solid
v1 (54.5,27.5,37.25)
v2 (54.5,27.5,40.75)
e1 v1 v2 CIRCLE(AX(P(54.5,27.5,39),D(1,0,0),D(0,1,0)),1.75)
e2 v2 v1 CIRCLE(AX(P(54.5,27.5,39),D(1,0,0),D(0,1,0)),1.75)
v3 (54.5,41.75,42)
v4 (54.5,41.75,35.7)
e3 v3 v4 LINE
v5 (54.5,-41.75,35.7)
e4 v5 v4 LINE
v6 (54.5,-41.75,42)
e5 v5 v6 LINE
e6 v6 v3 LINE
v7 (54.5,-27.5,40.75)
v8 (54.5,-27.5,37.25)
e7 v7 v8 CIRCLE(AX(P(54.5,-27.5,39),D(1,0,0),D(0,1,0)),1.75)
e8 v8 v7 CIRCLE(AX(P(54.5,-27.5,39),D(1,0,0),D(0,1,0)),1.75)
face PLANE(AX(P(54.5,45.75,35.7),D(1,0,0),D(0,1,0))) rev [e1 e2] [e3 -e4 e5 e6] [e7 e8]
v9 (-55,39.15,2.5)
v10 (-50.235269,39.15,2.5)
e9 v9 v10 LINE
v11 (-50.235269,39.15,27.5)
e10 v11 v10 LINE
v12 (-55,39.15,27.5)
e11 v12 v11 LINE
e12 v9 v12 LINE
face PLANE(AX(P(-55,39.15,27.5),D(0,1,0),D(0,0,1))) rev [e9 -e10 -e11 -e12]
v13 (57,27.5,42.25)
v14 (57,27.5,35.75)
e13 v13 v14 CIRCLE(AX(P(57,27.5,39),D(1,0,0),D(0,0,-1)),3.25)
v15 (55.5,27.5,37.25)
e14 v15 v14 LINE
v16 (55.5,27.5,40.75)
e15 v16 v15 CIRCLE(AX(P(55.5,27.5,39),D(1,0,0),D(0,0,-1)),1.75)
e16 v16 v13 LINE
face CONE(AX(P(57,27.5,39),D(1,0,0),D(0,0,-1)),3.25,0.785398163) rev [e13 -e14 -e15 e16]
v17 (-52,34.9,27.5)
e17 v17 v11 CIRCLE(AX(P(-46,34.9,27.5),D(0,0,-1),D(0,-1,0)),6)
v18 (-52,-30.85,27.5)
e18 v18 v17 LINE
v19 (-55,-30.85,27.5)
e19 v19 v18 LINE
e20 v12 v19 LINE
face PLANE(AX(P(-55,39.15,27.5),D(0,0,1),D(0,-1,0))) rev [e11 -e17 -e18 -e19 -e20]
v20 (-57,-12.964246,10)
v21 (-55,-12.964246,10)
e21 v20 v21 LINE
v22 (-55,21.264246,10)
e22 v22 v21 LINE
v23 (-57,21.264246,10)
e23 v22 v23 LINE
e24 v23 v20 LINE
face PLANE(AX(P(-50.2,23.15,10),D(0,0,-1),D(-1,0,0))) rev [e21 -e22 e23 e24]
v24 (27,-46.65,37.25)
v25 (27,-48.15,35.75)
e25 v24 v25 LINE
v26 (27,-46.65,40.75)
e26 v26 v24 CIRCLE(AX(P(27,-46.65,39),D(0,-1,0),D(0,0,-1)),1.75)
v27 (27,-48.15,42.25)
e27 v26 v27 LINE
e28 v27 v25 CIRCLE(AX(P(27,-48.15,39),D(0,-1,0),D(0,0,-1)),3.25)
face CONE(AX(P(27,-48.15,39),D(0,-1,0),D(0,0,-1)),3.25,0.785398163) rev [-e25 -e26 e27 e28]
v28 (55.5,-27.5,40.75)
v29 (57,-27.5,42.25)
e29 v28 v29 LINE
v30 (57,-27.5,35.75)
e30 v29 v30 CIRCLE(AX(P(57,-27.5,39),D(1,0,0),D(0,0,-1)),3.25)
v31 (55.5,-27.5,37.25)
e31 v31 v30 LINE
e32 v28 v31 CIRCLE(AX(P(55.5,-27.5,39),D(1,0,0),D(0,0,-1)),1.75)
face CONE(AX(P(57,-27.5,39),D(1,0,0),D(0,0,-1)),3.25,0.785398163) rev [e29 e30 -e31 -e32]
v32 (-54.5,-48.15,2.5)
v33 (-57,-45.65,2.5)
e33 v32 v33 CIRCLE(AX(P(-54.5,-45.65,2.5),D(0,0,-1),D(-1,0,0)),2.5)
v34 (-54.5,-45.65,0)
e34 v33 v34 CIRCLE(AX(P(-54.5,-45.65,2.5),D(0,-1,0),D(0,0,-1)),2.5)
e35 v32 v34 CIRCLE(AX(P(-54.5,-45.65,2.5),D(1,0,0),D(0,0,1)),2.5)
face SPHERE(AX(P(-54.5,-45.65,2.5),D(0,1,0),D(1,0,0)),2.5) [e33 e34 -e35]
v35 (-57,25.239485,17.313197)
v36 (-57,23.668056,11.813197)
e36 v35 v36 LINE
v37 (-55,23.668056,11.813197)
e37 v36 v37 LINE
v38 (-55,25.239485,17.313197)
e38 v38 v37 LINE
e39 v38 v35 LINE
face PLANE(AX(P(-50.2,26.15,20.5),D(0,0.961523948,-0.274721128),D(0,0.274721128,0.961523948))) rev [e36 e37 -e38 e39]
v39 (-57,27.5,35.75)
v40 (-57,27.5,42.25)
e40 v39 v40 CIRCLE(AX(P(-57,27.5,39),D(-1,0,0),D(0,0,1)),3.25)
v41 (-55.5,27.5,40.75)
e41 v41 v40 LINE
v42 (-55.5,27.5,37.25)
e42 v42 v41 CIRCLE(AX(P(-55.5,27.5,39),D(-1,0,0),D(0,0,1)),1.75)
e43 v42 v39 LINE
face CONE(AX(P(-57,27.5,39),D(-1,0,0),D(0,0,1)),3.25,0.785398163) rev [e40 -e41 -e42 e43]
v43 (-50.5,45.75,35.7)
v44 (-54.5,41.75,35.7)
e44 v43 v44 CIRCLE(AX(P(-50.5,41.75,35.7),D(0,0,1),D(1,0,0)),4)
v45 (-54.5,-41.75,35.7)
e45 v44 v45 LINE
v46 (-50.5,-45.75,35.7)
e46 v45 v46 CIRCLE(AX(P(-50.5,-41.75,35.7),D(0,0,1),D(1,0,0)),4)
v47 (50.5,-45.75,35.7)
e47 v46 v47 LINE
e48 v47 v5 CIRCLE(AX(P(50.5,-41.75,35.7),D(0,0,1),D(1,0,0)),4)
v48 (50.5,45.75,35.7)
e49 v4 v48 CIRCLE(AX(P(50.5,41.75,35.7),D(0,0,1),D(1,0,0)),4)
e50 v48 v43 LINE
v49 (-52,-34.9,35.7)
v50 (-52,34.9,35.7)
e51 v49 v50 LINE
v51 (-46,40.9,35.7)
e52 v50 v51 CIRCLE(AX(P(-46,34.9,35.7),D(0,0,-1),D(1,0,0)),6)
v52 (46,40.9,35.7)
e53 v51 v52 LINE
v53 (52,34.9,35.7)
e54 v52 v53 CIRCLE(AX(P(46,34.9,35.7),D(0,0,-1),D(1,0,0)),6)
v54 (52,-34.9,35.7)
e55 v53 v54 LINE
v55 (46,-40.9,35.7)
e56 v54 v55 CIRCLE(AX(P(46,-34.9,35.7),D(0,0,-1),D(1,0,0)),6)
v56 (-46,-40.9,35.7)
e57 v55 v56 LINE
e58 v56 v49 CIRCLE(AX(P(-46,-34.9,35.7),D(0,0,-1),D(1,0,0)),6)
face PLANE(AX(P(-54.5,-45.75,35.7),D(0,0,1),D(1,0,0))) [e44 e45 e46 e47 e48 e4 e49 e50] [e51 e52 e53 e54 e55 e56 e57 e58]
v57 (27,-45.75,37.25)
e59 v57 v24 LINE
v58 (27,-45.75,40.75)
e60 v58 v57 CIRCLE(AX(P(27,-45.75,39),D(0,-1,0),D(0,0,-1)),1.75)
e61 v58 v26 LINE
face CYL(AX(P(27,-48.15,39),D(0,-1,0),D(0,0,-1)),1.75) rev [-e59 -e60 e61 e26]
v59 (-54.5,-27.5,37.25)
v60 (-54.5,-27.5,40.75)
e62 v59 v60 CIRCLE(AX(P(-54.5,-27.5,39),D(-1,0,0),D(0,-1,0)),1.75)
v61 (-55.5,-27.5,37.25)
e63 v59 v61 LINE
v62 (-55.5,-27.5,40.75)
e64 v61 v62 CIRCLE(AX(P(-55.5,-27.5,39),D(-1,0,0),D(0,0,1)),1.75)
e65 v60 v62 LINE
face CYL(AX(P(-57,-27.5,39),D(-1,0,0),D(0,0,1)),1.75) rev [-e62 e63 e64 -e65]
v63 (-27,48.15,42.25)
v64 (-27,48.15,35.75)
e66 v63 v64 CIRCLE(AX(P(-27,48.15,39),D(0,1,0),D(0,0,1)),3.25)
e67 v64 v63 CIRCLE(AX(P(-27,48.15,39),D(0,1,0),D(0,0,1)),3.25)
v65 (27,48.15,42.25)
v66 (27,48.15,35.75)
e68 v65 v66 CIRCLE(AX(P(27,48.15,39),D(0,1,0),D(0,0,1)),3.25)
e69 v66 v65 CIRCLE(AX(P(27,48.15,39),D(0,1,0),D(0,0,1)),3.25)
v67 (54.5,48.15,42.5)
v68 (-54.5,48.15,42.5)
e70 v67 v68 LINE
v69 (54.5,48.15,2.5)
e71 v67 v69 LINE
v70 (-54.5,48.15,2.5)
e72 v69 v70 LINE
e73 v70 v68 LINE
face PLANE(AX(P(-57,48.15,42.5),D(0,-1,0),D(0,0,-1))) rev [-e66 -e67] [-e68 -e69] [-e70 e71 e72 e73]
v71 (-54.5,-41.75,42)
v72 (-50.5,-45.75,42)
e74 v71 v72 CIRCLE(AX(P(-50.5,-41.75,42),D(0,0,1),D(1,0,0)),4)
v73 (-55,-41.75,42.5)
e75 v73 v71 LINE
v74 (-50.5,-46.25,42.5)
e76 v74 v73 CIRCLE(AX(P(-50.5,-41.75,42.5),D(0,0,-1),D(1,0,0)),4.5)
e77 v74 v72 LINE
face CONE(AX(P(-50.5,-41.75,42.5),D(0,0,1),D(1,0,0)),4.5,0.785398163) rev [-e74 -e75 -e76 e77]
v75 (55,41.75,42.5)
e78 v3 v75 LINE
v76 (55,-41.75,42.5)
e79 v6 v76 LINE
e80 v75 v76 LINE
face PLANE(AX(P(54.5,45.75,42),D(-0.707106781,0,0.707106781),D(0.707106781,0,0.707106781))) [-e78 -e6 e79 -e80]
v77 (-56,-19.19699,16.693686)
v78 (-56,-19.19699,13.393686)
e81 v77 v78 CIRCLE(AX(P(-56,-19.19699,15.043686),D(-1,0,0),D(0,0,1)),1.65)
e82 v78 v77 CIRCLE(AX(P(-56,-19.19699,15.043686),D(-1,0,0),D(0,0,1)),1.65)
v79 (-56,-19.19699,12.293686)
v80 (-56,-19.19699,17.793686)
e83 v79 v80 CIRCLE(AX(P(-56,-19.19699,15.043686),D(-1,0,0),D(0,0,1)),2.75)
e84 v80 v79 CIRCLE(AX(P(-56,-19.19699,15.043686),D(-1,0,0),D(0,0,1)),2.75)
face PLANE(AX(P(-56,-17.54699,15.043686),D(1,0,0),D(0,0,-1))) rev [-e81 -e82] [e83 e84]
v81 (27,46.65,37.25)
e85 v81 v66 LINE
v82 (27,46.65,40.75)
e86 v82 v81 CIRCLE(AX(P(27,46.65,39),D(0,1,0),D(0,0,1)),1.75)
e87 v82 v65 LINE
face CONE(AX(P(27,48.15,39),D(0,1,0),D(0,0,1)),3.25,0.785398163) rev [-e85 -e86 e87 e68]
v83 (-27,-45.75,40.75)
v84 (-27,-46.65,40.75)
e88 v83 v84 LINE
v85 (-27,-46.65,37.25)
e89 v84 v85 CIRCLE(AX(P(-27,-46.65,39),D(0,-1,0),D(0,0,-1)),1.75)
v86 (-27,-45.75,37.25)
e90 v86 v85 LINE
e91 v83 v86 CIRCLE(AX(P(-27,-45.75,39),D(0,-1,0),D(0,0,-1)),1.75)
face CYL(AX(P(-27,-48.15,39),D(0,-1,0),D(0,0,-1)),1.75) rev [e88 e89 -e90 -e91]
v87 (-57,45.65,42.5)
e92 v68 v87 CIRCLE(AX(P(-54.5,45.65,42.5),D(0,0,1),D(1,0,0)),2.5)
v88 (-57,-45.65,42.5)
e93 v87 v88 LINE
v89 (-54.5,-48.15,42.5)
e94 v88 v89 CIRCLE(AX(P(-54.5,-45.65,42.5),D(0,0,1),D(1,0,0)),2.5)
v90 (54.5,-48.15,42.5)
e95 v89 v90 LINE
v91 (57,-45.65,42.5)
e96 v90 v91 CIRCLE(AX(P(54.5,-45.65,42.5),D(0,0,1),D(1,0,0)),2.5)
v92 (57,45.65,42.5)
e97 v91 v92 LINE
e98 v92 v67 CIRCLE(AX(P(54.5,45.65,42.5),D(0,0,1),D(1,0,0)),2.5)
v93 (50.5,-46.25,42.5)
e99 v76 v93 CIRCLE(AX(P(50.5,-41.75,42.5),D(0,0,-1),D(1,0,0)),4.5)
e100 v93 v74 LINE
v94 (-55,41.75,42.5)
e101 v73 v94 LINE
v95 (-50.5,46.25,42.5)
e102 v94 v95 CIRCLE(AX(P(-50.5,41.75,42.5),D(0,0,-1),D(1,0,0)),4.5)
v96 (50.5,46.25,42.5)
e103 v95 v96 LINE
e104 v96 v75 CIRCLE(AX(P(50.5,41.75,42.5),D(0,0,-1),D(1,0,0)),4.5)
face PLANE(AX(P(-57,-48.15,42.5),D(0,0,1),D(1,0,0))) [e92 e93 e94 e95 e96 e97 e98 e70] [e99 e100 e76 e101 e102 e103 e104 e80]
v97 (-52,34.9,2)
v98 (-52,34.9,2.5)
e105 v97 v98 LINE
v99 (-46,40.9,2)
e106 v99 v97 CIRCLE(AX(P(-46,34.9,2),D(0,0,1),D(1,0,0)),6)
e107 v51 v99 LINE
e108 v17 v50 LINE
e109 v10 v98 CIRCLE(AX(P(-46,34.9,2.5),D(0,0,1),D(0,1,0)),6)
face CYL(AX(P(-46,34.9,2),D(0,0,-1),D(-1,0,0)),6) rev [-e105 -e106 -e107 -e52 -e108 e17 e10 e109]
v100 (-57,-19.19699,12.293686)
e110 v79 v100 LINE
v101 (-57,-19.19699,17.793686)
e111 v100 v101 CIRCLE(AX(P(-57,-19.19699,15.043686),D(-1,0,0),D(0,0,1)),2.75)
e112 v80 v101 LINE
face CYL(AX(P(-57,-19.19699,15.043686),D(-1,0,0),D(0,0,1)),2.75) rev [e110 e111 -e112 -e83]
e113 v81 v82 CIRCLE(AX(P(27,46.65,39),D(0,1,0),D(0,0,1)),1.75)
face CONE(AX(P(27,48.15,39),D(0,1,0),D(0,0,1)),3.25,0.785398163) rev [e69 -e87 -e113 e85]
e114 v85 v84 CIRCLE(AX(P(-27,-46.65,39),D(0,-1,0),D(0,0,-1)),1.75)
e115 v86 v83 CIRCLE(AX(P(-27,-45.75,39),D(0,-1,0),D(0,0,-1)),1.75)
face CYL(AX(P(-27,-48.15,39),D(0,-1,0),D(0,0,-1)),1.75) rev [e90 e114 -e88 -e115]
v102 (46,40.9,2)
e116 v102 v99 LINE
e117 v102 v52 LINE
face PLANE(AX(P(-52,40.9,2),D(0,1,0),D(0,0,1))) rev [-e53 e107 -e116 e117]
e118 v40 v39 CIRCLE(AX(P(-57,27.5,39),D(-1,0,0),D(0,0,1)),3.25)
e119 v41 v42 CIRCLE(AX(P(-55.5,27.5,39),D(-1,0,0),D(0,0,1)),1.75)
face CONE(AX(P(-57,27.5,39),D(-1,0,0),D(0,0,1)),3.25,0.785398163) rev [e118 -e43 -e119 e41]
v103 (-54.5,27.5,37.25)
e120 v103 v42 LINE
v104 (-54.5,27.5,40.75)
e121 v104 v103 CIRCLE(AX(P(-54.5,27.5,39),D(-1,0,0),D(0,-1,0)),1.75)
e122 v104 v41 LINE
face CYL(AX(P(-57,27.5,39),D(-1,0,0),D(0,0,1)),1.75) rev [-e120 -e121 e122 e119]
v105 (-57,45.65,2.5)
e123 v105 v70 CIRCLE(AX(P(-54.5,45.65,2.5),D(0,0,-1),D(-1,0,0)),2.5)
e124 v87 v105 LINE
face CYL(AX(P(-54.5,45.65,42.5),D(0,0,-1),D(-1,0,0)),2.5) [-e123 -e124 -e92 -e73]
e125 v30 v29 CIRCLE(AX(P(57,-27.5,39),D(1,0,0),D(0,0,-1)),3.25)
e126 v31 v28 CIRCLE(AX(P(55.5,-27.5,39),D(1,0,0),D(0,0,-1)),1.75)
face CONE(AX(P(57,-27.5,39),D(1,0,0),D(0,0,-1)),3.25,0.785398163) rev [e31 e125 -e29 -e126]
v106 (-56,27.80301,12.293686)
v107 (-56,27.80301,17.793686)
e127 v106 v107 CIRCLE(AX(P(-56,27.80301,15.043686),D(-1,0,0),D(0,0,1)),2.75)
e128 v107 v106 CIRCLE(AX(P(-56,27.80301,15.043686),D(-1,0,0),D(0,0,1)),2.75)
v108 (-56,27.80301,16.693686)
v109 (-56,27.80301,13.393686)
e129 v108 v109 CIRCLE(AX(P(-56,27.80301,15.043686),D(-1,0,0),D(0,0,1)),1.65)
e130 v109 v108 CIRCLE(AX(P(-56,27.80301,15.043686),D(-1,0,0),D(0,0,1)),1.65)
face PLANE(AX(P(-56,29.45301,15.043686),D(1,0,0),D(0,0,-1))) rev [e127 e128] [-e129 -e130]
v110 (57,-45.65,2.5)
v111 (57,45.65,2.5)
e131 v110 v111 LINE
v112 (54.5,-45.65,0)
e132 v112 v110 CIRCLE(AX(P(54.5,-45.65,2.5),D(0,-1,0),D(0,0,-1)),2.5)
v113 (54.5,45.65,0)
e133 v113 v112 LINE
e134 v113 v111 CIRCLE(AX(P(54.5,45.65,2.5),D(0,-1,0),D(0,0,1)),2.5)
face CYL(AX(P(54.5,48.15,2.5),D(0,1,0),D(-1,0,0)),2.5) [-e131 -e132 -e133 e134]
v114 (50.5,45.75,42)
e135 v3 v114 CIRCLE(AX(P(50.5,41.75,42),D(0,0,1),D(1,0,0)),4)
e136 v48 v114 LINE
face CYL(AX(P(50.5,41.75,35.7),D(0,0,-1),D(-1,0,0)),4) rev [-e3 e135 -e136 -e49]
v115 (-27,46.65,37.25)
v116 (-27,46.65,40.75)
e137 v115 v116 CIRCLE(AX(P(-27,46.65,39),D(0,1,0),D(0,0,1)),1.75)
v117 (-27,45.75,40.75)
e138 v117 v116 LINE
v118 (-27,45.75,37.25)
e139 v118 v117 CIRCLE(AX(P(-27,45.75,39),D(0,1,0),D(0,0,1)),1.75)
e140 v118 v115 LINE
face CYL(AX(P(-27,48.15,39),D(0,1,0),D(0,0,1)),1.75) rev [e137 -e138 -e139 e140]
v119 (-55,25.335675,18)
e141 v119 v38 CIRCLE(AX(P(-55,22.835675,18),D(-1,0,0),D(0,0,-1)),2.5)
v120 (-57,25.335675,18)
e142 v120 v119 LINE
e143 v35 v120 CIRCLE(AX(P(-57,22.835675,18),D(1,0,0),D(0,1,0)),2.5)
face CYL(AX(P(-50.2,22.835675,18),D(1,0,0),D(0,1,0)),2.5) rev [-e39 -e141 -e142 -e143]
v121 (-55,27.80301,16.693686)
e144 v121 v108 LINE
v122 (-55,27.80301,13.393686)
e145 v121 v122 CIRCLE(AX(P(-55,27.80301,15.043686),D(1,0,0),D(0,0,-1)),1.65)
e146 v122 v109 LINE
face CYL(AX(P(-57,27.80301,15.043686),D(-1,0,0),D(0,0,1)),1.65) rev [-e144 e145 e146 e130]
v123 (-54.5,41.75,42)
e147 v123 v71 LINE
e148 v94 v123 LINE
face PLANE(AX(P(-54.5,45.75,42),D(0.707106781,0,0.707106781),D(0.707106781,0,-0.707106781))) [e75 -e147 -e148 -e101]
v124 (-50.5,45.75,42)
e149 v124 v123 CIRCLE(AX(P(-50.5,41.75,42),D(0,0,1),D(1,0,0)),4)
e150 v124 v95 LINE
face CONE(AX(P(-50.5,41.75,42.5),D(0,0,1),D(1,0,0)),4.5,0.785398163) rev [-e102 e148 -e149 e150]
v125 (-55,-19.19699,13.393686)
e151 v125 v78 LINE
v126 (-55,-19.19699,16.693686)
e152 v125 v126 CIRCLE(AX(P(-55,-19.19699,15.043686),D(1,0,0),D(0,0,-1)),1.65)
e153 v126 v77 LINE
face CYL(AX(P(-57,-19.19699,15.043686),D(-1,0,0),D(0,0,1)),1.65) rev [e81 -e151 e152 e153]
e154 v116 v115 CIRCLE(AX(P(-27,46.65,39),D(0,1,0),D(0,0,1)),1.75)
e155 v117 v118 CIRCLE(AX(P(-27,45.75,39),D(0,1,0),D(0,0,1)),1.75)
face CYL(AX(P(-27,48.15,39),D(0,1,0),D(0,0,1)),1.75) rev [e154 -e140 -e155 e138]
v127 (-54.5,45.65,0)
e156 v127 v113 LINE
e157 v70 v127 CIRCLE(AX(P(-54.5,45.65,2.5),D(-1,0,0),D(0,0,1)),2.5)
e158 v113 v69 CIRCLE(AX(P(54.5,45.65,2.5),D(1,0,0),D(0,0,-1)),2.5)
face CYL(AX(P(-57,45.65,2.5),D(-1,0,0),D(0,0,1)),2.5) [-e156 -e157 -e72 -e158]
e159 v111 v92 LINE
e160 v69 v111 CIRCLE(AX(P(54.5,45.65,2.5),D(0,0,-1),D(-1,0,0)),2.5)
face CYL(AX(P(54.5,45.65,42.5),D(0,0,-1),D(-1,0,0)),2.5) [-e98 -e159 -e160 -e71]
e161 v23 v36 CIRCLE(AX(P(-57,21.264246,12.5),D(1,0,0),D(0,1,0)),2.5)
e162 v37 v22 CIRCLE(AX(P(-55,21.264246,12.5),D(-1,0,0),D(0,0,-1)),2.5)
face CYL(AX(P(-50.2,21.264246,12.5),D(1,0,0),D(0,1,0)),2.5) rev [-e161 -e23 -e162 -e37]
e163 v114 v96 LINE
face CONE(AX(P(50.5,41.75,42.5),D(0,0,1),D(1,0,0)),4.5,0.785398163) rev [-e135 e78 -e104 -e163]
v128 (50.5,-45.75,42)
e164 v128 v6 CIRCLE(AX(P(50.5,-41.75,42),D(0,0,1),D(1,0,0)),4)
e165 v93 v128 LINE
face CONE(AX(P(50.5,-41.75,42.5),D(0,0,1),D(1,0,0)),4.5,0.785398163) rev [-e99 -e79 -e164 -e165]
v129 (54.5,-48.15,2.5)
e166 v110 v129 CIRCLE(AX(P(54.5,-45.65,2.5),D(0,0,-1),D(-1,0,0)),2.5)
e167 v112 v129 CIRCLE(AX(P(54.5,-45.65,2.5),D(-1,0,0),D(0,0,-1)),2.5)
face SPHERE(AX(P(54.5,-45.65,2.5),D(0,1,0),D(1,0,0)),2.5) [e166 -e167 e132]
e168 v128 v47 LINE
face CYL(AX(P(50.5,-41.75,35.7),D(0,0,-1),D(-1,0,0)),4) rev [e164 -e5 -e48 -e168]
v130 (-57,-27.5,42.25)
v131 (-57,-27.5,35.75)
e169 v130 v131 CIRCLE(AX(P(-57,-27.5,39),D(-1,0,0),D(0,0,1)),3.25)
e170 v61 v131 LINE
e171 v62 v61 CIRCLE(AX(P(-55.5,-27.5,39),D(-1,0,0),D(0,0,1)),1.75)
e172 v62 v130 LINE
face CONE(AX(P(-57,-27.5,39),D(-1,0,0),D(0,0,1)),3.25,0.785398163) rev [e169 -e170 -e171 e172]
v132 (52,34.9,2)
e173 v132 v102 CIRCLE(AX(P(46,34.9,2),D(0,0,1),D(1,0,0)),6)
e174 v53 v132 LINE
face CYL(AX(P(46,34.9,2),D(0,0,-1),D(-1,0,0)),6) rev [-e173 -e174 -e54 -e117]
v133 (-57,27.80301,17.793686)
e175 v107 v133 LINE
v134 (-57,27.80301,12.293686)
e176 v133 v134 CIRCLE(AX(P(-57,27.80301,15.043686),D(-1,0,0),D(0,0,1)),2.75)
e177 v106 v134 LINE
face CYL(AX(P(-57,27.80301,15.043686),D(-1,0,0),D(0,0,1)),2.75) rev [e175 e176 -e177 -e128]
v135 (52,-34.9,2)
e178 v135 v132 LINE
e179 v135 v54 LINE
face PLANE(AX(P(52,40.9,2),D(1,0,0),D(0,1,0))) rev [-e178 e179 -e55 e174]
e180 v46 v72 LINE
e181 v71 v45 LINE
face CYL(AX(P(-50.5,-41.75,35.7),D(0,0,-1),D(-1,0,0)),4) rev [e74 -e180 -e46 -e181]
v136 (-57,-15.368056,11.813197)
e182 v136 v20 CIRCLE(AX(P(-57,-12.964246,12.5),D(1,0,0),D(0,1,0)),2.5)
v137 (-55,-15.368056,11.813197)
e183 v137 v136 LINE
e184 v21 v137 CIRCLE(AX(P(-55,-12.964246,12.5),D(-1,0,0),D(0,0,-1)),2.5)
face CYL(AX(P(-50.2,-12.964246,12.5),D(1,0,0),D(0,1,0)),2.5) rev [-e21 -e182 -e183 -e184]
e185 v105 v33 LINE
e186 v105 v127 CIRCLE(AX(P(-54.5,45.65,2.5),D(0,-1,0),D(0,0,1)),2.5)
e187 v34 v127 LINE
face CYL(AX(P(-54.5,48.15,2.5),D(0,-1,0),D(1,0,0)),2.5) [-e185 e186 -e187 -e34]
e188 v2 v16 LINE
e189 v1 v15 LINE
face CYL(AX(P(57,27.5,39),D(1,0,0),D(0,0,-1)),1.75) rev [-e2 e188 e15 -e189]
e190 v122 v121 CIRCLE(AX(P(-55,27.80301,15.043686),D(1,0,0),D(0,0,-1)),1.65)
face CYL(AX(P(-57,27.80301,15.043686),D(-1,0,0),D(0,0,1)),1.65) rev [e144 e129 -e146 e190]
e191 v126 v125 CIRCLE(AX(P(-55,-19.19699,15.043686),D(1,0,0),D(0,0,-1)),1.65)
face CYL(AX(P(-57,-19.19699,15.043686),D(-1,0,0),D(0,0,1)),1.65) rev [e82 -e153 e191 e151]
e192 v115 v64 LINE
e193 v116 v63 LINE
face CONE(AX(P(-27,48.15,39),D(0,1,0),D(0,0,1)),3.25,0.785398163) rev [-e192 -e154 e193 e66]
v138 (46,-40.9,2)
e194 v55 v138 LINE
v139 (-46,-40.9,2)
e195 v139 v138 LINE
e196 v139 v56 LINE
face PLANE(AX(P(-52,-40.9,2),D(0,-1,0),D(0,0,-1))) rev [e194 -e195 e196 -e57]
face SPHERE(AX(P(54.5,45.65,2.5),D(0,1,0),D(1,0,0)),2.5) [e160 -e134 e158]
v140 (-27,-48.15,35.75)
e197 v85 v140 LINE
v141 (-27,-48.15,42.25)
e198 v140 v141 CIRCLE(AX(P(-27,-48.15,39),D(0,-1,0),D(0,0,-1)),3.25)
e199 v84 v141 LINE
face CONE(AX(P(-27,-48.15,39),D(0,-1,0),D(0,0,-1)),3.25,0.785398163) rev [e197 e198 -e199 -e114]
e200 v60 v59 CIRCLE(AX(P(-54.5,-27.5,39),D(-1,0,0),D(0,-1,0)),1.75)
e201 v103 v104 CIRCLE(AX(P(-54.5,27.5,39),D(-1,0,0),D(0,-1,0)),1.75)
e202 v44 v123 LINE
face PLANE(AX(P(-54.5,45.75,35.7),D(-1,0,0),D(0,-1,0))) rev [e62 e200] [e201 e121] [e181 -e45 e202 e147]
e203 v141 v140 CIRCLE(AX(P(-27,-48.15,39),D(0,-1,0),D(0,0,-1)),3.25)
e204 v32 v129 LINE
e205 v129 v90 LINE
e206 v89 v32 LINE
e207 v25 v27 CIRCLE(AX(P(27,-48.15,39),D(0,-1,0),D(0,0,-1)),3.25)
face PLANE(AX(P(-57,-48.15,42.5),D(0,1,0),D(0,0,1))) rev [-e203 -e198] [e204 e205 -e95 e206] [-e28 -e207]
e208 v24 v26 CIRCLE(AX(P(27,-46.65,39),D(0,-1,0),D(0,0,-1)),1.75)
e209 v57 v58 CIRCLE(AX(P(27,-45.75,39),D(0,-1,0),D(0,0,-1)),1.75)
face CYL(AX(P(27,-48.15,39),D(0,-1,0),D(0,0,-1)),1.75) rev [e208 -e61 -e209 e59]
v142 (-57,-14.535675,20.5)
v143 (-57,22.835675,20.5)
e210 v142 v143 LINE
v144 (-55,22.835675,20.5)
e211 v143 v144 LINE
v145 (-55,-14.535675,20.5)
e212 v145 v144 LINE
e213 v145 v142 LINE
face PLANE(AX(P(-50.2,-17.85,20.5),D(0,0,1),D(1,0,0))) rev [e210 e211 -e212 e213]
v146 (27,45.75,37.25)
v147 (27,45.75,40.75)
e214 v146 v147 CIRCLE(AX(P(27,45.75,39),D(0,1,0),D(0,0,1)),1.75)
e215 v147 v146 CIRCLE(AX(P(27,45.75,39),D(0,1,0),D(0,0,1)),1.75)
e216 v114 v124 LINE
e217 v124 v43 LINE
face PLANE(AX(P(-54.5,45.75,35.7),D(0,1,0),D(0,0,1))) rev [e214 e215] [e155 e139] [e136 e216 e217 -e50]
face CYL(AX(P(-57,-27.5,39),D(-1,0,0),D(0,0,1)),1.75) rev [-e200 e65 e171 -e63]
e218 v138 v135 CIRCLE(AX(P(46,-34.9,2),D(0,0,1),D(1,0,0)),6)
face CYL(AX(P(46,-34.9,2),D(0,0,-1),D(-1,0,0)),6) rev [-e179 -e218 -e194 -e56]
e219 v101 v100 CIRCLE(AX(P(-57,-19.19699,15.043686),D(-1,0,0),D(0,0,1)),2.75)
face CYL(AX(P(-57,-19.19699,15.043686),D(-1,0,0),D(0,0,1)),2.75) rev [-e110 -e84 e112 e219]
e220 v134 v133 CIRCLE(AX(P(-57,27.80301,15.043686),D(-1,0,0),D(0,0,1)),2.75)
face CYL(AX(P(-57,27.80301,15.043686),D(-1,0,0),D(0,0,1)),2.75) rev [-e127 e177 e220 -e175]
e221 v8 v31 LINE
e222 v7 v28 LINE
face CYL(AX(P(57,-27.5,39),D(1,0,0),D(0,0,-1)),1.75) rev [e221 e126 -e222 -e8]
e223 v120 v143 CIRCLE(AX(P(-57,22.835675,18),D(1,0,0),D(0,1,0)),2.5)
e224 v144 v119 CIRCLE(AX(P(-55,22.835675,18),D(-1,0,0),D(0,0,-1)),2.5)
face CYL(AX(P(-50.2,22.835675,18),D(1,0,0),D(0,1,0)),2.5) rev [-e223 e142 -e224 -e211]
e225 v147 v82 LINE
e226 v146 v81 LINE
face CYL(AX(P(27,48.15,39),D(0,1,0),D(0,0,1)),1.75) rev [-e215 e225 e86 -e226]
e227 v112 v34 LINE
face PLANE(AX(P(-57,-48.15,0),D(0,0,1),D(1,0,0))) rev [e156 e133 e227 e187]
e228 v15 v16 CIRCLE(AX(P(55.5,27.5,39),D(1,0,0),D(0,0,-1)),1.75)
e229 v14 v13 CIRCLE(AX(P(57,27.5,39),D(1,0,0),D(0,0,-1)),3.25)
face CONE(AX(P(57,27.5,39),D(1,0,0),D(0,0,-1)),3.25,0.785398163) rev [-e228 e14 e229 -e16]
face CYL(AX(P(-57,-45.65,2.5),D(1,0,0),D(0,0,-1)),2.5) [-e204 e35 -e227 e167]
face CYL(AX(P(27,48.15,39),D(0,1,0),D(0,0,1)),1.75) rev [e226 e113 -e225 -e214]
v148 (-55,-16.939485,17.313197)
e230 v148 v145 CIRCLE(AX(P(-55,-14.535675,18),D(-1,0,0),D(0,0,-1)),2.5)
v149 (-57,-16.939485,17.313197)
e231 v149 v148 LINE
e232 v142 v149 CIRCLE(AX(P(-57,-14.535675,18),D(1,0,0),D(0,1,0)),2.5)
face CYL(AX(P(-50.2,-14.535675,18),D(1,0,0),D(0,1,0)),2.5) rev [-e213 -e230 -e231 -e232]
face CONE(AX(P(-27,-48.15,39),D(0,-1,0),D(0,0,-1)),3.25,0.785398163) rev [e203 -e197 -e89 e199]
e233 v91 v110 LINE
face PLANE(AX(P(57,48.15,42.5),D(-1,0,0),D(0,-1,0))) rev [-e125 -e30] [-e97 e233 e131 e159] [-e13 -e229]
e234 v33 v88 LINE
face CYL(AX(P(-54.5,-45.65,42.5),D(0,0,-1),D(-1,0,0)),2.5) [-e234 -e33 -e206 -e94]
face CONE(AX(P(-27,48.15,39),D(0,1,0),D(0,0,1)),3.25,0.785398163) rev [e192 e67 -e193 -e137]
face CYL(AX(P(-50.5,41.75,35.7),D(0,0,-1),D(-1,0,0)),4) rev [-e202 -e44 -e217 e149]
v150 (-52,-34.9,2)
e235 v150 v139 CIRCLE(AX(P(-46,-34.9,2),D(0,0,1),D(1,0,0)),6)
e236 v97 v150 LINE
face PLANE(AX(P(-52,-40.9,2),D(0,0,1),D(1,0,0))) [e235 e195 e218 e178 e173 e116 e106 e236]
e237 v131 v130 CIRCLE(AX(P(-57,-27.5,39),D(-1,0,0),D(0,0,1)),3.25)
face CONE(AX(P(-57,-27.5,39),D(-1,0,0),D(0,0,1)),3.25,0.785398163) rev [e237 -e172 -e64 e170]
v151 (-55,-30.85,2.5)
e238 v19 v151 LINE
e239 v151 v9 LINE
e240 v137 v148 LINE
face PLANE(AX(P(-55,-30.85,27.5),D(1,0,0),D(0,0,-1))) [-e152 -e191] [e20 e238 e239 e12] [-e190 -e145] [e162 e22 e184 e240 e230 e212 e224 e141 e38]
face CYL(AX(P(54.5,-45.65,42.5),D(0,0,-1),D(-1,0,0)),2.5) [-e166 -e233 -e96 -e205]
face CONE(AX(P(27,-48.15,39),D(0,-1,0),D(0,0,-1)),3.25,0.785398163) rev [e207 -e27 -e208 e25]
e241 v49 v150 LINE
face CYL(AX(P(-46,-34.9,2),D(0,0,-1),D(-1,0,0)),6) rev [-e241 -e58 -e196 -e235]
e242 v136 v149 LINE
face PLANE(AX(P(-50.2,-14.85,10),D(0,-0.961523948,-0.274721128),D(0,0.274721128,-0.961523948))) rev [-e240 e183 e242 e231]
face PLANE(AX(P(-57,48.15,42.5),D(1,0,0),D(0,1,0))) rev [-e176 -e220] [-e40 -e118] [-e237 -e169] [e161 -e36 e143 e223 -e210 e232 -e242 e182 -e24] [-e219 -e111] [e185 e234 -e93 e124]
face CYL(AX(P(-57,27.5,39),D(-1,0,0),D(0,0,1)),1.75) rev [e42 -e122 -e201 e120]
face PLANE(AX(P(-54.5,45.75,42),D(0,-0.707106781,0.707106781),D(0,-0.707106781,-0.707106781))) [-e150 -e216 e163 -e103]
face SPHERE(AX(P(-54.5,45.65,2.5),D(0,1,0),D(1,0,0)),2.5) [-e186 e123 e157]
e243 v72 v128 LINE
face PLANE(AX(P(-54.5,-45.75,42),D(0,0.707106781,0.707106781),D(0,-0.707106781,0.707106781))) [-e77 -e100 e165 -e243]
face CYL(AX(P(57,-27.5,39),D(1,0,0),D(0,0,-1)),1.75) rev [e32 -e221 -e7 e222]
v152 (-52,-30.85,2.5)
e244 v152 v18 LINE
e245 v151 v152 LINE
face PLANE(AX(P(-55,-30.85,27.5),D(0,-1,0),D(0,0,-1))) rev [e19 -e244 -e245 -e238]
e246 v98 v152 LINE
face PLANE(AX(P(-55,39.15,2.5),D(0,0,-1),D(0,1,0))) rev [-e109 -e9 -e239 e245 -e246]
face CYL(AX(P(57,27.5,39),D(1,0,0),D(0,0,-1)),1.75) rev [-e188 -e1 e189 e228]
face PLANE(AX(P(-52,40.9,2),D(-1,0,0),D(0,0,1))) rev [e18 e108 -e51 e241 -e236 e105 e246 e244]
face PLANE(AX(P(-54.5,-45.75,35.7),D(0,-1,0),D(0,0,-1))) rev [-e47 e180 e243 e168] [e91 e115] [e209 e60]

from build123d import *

# Parameters (mm, degrees)
SKETCH_1_W                  = 114
SKETCH_1_H                  = 96.3
EXTRUDE_1_DEPTH             = 42.5
SKETCH_2_W                  = 104
SKETCH_2_H                  = 81.8
CUT_EXTRUDE_1_DEPTH         = 40.5
SKETCH_3_W                  = 109
SKETCH_3_H                  = 91.5
CUT_EXTRUDE_2_DEPTH         = 6.8
FILLET_1_R                  = 2.5
FILLET_2_R                  = 4
FILLET_3_R                  = 6
HOLE_WIZARD_1_D             = 3.5
HOLE_WIZARD_1_DEPTH         = 10
HOLE_WIZARD_1_CSINK_D       = 6.5
HOLE_WIZARD_1_CSINK_ANGLE   = 90
PATTERN_LINEAR_1_COUNT      = 2
PATTERN_LINEAR_1_PITCH      = 54
MIRROR_1_COPY_1_D           = 3.5
MIRROR_1_COPY_1_DEPTH       = 10
MIRROR_1_COPY_1_CSINK_D     = 6.5
MIRROR_1_COPY_1_CSINK_ANGLE = 90
HOLE_WIZARD_2_D             = 3.5
HOLE_WIZARD_2_DEPTH         = 10
HOLE_WIZARD_2_CSINK_D       = 6.5
HOLE_WIZARD_2_CSINK_ANGLE   = 90
PATTERN_LINEAR_2_COUNT      = 2
PATTERN_LINEAR_2_PITCH      = 55
MIRROR_2_COPY_1_D           = 3.5
MIRROR_2_COPY_1_DEPTH       = 10
MIRROR_2_COPY_1_CSINK_D     = 6.5
MIRROR_2_COPY_1_CSINK_ANGLE = 90
CUT_EXTRUDE_3_DEPTH         = 6.8
FILLET_4_R                  = 2.5
SKETCH_8_W                  = 25
SKETCH_8_H                  = 70
CUT_EXTRUDE_4_DEPTH         = 3
HOLE_WIZARD_3_D             = 3.3
HOLE_WIZARD_3_DEPTH         = 10
HOLE_WIZARD_3_CBORE_D       = 5.5
HOLE_WIZARD_3_CBORE_DEPTH   = 1
PATTERN_LINEAR_3_COUNT      = 2
PATTERN_LINEAR_3_PITCH      = 47
CHAMFER_1_SIZE              = 0.5


with BuildPart() as part:
    # 草图1 → 拉伸1 (new body)
    with BuildSketch(Plane.XY):
        Rectangle(SKETCH_1_W, SKETCH_1_H)
    extrude(amount=EXTRUDE_1_DEPTH)

    # 草图2 → 切除-拉伸1 (cut)
    with BuildSketch(Plane.XY.offset(42.5)):
        Rectangle(SKETCH_2_W, SKETCH_2_H)
    extrude(amount=-CUT_EXTRUDE_1_DEPTH, mode=Mode.SUBTRACT)

    # 草图3 → 切除-拉伸2 (cut)
    with BuildSketch(Plane.XY.offset(42.5)):
        Rectangle(SKETCH_3_W, SKETCH_3_H)
    extrude(amount=-CUT_EXTRUDE_2_DEPTH, mode=Mode.SUBTRACT)

    # 圆角1
    fillet_1_edges = [part.edges().sort_by_distance(p)[0] for p in [
        (0, 48.15, 0),
        (57, 0, 0),
        (0, -48.15, 0),
        (-57, 0, 0),
        (-57, 48.15, 21.25),
        (57, 48.15, 21.25),
        (57, -48.15, 21.25),
        (-57, -48.15, 21.25),
    ]]
    fillet(fillet_1_edges, radius=FILLET_1_R)

    # 圆角2
    fillet_2_edges = [part.edges().sort_by_distance(p)[0] for p in [
        (-54.5, -45.75, 39.1),
        (-54.5, 45.75, 39.1),
        (54.5, 45.75, 39.1),
        (54.5, -45.75, 39.1),
    ]]
    fillet(fillet_2_edges, radius=FILLET_2_R)

    # 圆角3
    fillet_3_edges = [part.edges().sort_by_distance(p)[0] for p in [
        (-52, -40.9, 18.85),
        (-52, 40.9, 18.85),
        (52, 40.9, 18.85),
        (52, -40.9, 18.85),
    ]]
    fillet(fillet_3_edges, radius=FILLET_3_R)

    # 孔1
    with Locations(Plane(origin=(27, 48.15, 39), x_dir=(0, 0, 1), z_dir=(0, 1, 0))):
        with Locations((0, 0)):
            hole_wizard_1 = CounterSinkHole(HOLE_WIZARD_1_D / 2, HOLE_WIZARD_1_CSINK_D / 2, depth=HOLE_WIZARD_1_DEPTH, counter_sink_angle=HOLE_WIZARD_1_CSINK_ANGLE)

    # 阵列(线性)1: 孔1 ×2
    with Locations(*[(-i * PATTERN_LINEAR_1_PITCH, 0, 0) for i in range(1, PATTERN_LINEAR_1_COUNT)]):
        add(hole_wizard_1, mode=Mode.SUBTRACT)

    # 镜向1: 孔1 across plane
    add(hole_wizard_1.mirror(Plane.ZX), mode=Mode.SUBTRACT)

    # 镜向1 copy 1
    with Locations(Plane(origin=(-27, -48.15, 39), x_dir=(0, 0, 1), z_dir=(0, -1, 0))):
        with Locations((0, 0)):
            CounterSinkHole(MIRROR_1_COPY_1_D / 2, MIRROR_1_COPY_1_CSINK_D / 2, depth=MIRROR_1_COPY_1_DEPTH, counter_sink_angle=MIRROR_1_COPY_1_CSINK_ANGLE)

    # 孔2
    with Locations(Plane(origin=(-57, 27.5, 39), x_dir=(0, -1, 0), z_dir=(-1, 0, 0))):
        with Locations((0, 0)):
            hole_wizard_2 = CounterSinkHole(HOLE_WIZARD_2_D / 2, HOLE_WIZARD_2_CSINK_D / 2, depth=HOLE_WIZARD_2_DEPTH, counter_sink_angle=HOLE_WIZARD_2_CSINK_ANGLE)

    # 阵列(线性)2: 孔2 ×2
    with Locations(*[(0, -i * PATTERN_LINEAR_2_PITCH, 0) for i in range(1, PATTERN_LINEAR_2_COUNT)]):
        add(hole_wizard_2, mode=Mode.SUBTRACT)

    # 镜向2: 孔2 across plane
    add(hole_wizard_2.mirror(Plane(origin=(0, 0, 0), x_dir=(0, 0, 1), z_dir=(1, 0, 0))), mode=Mode.SUBTRACT)

    # 镜向2 copy 1
    with Locations(Plane(origin=(57, -27.5, 39), x_dir=(0, -1, 0), z_dir=(1, 0, 0))):
        with Locations((0, 0)):
            CounterSinkHole(MIRROR_2_COPY_1_D / 2, MIRROR_2_COPY_1_CSINK_D / 2, depth=MIRROR_2_COPY_1_DEPTH, counter_sink_angle=MIRROR_2_COPY_1_CSINK_ANGLE)

    # 草图7 → 切除-拉伸3 (cut)
    with BuildSketch(Plane.ZY.offset(57)):
        Polygon((10, 23.15), (10, -14.85), (20.5, -17.85), (20.5, 26.15), align=None)
    extrude(amount=-CUT_EXTRUDE_3_DEPTH, mode=Mode.SUBTRACT)

    # 圆角4
    fillet_4_edges = [part.edges().sort_by_distance(p)[0] for p in [
        (-54.5, 23.15, 10),
        (-54.5, 26.15, 20.5),
        (-54.5, -17.85, 20.5),
        (-54.5, -14.85, 10),
    ]]
    fillet(fillet_4_edges, radius=FILLET_4_R)

    # 草图8 → 切除-拉伸4 (cut, symmetric)
    with BuildSketch(Plane(origin=(-52, 0, 0), x_dir=(0, 0, -1), z_dir=(1, 0, 0))):
        with Locations((-15, 4.15)):
            Rectangle(SKETCH_8_W, SKETCH_8_H)
    extrude(amount=CUT_EXTRUDE_4_DEPTH, both=True, mode=Mode.SUBTRACT)

    # 孔3
    with Locations(Plane(origin=(-57, 27.803010051, 15.043686383), x_dir=(0, -1, 0), z_dir=(-1, 0, 0))):
        with Locations((0, 0)):
            hole_wizard_3 = CounterBoreHole(HOLE_WIZARD_3_D / 2, HOLE_WIZARD_3_CBORE_D / 2, HOLE_WIZARD_3_CBORE_DEPTH, depth=HOLE_WIZARD_3_DEPTH)

    # 阵列(线性)3: 孔3 ×2
    with Locations(*[(0, -i * PATTERN_LINEAR_3_PITCH, 0) for i in range(1, PATTERN_LINEAR_3_COUNT)]):
        add(hole_wizard_3, mode=Mode.SUBTRACT)

    # 倒角1
    chamfer_1_edges = [part.edges().sort_by_distance(p)[0] for p in [
        (0, 45.75, 42.5),
        (54.5, 0, 42.5),
        (-54.5, 0, 42.5),
        (0, -45.75, 42.5),
        (53.328427125, 44.578427125, 42.5),
        (-53.328427125, 44.578427125, 42.5),
        (-53.328427125, -44.578427125, 42.5),
        (53.328427125, -44.578427125, 42.5),
    ]]
    chamfer(chamfer_1_edges, length=CHAMFER_1_SIZE)


solid = part.part
